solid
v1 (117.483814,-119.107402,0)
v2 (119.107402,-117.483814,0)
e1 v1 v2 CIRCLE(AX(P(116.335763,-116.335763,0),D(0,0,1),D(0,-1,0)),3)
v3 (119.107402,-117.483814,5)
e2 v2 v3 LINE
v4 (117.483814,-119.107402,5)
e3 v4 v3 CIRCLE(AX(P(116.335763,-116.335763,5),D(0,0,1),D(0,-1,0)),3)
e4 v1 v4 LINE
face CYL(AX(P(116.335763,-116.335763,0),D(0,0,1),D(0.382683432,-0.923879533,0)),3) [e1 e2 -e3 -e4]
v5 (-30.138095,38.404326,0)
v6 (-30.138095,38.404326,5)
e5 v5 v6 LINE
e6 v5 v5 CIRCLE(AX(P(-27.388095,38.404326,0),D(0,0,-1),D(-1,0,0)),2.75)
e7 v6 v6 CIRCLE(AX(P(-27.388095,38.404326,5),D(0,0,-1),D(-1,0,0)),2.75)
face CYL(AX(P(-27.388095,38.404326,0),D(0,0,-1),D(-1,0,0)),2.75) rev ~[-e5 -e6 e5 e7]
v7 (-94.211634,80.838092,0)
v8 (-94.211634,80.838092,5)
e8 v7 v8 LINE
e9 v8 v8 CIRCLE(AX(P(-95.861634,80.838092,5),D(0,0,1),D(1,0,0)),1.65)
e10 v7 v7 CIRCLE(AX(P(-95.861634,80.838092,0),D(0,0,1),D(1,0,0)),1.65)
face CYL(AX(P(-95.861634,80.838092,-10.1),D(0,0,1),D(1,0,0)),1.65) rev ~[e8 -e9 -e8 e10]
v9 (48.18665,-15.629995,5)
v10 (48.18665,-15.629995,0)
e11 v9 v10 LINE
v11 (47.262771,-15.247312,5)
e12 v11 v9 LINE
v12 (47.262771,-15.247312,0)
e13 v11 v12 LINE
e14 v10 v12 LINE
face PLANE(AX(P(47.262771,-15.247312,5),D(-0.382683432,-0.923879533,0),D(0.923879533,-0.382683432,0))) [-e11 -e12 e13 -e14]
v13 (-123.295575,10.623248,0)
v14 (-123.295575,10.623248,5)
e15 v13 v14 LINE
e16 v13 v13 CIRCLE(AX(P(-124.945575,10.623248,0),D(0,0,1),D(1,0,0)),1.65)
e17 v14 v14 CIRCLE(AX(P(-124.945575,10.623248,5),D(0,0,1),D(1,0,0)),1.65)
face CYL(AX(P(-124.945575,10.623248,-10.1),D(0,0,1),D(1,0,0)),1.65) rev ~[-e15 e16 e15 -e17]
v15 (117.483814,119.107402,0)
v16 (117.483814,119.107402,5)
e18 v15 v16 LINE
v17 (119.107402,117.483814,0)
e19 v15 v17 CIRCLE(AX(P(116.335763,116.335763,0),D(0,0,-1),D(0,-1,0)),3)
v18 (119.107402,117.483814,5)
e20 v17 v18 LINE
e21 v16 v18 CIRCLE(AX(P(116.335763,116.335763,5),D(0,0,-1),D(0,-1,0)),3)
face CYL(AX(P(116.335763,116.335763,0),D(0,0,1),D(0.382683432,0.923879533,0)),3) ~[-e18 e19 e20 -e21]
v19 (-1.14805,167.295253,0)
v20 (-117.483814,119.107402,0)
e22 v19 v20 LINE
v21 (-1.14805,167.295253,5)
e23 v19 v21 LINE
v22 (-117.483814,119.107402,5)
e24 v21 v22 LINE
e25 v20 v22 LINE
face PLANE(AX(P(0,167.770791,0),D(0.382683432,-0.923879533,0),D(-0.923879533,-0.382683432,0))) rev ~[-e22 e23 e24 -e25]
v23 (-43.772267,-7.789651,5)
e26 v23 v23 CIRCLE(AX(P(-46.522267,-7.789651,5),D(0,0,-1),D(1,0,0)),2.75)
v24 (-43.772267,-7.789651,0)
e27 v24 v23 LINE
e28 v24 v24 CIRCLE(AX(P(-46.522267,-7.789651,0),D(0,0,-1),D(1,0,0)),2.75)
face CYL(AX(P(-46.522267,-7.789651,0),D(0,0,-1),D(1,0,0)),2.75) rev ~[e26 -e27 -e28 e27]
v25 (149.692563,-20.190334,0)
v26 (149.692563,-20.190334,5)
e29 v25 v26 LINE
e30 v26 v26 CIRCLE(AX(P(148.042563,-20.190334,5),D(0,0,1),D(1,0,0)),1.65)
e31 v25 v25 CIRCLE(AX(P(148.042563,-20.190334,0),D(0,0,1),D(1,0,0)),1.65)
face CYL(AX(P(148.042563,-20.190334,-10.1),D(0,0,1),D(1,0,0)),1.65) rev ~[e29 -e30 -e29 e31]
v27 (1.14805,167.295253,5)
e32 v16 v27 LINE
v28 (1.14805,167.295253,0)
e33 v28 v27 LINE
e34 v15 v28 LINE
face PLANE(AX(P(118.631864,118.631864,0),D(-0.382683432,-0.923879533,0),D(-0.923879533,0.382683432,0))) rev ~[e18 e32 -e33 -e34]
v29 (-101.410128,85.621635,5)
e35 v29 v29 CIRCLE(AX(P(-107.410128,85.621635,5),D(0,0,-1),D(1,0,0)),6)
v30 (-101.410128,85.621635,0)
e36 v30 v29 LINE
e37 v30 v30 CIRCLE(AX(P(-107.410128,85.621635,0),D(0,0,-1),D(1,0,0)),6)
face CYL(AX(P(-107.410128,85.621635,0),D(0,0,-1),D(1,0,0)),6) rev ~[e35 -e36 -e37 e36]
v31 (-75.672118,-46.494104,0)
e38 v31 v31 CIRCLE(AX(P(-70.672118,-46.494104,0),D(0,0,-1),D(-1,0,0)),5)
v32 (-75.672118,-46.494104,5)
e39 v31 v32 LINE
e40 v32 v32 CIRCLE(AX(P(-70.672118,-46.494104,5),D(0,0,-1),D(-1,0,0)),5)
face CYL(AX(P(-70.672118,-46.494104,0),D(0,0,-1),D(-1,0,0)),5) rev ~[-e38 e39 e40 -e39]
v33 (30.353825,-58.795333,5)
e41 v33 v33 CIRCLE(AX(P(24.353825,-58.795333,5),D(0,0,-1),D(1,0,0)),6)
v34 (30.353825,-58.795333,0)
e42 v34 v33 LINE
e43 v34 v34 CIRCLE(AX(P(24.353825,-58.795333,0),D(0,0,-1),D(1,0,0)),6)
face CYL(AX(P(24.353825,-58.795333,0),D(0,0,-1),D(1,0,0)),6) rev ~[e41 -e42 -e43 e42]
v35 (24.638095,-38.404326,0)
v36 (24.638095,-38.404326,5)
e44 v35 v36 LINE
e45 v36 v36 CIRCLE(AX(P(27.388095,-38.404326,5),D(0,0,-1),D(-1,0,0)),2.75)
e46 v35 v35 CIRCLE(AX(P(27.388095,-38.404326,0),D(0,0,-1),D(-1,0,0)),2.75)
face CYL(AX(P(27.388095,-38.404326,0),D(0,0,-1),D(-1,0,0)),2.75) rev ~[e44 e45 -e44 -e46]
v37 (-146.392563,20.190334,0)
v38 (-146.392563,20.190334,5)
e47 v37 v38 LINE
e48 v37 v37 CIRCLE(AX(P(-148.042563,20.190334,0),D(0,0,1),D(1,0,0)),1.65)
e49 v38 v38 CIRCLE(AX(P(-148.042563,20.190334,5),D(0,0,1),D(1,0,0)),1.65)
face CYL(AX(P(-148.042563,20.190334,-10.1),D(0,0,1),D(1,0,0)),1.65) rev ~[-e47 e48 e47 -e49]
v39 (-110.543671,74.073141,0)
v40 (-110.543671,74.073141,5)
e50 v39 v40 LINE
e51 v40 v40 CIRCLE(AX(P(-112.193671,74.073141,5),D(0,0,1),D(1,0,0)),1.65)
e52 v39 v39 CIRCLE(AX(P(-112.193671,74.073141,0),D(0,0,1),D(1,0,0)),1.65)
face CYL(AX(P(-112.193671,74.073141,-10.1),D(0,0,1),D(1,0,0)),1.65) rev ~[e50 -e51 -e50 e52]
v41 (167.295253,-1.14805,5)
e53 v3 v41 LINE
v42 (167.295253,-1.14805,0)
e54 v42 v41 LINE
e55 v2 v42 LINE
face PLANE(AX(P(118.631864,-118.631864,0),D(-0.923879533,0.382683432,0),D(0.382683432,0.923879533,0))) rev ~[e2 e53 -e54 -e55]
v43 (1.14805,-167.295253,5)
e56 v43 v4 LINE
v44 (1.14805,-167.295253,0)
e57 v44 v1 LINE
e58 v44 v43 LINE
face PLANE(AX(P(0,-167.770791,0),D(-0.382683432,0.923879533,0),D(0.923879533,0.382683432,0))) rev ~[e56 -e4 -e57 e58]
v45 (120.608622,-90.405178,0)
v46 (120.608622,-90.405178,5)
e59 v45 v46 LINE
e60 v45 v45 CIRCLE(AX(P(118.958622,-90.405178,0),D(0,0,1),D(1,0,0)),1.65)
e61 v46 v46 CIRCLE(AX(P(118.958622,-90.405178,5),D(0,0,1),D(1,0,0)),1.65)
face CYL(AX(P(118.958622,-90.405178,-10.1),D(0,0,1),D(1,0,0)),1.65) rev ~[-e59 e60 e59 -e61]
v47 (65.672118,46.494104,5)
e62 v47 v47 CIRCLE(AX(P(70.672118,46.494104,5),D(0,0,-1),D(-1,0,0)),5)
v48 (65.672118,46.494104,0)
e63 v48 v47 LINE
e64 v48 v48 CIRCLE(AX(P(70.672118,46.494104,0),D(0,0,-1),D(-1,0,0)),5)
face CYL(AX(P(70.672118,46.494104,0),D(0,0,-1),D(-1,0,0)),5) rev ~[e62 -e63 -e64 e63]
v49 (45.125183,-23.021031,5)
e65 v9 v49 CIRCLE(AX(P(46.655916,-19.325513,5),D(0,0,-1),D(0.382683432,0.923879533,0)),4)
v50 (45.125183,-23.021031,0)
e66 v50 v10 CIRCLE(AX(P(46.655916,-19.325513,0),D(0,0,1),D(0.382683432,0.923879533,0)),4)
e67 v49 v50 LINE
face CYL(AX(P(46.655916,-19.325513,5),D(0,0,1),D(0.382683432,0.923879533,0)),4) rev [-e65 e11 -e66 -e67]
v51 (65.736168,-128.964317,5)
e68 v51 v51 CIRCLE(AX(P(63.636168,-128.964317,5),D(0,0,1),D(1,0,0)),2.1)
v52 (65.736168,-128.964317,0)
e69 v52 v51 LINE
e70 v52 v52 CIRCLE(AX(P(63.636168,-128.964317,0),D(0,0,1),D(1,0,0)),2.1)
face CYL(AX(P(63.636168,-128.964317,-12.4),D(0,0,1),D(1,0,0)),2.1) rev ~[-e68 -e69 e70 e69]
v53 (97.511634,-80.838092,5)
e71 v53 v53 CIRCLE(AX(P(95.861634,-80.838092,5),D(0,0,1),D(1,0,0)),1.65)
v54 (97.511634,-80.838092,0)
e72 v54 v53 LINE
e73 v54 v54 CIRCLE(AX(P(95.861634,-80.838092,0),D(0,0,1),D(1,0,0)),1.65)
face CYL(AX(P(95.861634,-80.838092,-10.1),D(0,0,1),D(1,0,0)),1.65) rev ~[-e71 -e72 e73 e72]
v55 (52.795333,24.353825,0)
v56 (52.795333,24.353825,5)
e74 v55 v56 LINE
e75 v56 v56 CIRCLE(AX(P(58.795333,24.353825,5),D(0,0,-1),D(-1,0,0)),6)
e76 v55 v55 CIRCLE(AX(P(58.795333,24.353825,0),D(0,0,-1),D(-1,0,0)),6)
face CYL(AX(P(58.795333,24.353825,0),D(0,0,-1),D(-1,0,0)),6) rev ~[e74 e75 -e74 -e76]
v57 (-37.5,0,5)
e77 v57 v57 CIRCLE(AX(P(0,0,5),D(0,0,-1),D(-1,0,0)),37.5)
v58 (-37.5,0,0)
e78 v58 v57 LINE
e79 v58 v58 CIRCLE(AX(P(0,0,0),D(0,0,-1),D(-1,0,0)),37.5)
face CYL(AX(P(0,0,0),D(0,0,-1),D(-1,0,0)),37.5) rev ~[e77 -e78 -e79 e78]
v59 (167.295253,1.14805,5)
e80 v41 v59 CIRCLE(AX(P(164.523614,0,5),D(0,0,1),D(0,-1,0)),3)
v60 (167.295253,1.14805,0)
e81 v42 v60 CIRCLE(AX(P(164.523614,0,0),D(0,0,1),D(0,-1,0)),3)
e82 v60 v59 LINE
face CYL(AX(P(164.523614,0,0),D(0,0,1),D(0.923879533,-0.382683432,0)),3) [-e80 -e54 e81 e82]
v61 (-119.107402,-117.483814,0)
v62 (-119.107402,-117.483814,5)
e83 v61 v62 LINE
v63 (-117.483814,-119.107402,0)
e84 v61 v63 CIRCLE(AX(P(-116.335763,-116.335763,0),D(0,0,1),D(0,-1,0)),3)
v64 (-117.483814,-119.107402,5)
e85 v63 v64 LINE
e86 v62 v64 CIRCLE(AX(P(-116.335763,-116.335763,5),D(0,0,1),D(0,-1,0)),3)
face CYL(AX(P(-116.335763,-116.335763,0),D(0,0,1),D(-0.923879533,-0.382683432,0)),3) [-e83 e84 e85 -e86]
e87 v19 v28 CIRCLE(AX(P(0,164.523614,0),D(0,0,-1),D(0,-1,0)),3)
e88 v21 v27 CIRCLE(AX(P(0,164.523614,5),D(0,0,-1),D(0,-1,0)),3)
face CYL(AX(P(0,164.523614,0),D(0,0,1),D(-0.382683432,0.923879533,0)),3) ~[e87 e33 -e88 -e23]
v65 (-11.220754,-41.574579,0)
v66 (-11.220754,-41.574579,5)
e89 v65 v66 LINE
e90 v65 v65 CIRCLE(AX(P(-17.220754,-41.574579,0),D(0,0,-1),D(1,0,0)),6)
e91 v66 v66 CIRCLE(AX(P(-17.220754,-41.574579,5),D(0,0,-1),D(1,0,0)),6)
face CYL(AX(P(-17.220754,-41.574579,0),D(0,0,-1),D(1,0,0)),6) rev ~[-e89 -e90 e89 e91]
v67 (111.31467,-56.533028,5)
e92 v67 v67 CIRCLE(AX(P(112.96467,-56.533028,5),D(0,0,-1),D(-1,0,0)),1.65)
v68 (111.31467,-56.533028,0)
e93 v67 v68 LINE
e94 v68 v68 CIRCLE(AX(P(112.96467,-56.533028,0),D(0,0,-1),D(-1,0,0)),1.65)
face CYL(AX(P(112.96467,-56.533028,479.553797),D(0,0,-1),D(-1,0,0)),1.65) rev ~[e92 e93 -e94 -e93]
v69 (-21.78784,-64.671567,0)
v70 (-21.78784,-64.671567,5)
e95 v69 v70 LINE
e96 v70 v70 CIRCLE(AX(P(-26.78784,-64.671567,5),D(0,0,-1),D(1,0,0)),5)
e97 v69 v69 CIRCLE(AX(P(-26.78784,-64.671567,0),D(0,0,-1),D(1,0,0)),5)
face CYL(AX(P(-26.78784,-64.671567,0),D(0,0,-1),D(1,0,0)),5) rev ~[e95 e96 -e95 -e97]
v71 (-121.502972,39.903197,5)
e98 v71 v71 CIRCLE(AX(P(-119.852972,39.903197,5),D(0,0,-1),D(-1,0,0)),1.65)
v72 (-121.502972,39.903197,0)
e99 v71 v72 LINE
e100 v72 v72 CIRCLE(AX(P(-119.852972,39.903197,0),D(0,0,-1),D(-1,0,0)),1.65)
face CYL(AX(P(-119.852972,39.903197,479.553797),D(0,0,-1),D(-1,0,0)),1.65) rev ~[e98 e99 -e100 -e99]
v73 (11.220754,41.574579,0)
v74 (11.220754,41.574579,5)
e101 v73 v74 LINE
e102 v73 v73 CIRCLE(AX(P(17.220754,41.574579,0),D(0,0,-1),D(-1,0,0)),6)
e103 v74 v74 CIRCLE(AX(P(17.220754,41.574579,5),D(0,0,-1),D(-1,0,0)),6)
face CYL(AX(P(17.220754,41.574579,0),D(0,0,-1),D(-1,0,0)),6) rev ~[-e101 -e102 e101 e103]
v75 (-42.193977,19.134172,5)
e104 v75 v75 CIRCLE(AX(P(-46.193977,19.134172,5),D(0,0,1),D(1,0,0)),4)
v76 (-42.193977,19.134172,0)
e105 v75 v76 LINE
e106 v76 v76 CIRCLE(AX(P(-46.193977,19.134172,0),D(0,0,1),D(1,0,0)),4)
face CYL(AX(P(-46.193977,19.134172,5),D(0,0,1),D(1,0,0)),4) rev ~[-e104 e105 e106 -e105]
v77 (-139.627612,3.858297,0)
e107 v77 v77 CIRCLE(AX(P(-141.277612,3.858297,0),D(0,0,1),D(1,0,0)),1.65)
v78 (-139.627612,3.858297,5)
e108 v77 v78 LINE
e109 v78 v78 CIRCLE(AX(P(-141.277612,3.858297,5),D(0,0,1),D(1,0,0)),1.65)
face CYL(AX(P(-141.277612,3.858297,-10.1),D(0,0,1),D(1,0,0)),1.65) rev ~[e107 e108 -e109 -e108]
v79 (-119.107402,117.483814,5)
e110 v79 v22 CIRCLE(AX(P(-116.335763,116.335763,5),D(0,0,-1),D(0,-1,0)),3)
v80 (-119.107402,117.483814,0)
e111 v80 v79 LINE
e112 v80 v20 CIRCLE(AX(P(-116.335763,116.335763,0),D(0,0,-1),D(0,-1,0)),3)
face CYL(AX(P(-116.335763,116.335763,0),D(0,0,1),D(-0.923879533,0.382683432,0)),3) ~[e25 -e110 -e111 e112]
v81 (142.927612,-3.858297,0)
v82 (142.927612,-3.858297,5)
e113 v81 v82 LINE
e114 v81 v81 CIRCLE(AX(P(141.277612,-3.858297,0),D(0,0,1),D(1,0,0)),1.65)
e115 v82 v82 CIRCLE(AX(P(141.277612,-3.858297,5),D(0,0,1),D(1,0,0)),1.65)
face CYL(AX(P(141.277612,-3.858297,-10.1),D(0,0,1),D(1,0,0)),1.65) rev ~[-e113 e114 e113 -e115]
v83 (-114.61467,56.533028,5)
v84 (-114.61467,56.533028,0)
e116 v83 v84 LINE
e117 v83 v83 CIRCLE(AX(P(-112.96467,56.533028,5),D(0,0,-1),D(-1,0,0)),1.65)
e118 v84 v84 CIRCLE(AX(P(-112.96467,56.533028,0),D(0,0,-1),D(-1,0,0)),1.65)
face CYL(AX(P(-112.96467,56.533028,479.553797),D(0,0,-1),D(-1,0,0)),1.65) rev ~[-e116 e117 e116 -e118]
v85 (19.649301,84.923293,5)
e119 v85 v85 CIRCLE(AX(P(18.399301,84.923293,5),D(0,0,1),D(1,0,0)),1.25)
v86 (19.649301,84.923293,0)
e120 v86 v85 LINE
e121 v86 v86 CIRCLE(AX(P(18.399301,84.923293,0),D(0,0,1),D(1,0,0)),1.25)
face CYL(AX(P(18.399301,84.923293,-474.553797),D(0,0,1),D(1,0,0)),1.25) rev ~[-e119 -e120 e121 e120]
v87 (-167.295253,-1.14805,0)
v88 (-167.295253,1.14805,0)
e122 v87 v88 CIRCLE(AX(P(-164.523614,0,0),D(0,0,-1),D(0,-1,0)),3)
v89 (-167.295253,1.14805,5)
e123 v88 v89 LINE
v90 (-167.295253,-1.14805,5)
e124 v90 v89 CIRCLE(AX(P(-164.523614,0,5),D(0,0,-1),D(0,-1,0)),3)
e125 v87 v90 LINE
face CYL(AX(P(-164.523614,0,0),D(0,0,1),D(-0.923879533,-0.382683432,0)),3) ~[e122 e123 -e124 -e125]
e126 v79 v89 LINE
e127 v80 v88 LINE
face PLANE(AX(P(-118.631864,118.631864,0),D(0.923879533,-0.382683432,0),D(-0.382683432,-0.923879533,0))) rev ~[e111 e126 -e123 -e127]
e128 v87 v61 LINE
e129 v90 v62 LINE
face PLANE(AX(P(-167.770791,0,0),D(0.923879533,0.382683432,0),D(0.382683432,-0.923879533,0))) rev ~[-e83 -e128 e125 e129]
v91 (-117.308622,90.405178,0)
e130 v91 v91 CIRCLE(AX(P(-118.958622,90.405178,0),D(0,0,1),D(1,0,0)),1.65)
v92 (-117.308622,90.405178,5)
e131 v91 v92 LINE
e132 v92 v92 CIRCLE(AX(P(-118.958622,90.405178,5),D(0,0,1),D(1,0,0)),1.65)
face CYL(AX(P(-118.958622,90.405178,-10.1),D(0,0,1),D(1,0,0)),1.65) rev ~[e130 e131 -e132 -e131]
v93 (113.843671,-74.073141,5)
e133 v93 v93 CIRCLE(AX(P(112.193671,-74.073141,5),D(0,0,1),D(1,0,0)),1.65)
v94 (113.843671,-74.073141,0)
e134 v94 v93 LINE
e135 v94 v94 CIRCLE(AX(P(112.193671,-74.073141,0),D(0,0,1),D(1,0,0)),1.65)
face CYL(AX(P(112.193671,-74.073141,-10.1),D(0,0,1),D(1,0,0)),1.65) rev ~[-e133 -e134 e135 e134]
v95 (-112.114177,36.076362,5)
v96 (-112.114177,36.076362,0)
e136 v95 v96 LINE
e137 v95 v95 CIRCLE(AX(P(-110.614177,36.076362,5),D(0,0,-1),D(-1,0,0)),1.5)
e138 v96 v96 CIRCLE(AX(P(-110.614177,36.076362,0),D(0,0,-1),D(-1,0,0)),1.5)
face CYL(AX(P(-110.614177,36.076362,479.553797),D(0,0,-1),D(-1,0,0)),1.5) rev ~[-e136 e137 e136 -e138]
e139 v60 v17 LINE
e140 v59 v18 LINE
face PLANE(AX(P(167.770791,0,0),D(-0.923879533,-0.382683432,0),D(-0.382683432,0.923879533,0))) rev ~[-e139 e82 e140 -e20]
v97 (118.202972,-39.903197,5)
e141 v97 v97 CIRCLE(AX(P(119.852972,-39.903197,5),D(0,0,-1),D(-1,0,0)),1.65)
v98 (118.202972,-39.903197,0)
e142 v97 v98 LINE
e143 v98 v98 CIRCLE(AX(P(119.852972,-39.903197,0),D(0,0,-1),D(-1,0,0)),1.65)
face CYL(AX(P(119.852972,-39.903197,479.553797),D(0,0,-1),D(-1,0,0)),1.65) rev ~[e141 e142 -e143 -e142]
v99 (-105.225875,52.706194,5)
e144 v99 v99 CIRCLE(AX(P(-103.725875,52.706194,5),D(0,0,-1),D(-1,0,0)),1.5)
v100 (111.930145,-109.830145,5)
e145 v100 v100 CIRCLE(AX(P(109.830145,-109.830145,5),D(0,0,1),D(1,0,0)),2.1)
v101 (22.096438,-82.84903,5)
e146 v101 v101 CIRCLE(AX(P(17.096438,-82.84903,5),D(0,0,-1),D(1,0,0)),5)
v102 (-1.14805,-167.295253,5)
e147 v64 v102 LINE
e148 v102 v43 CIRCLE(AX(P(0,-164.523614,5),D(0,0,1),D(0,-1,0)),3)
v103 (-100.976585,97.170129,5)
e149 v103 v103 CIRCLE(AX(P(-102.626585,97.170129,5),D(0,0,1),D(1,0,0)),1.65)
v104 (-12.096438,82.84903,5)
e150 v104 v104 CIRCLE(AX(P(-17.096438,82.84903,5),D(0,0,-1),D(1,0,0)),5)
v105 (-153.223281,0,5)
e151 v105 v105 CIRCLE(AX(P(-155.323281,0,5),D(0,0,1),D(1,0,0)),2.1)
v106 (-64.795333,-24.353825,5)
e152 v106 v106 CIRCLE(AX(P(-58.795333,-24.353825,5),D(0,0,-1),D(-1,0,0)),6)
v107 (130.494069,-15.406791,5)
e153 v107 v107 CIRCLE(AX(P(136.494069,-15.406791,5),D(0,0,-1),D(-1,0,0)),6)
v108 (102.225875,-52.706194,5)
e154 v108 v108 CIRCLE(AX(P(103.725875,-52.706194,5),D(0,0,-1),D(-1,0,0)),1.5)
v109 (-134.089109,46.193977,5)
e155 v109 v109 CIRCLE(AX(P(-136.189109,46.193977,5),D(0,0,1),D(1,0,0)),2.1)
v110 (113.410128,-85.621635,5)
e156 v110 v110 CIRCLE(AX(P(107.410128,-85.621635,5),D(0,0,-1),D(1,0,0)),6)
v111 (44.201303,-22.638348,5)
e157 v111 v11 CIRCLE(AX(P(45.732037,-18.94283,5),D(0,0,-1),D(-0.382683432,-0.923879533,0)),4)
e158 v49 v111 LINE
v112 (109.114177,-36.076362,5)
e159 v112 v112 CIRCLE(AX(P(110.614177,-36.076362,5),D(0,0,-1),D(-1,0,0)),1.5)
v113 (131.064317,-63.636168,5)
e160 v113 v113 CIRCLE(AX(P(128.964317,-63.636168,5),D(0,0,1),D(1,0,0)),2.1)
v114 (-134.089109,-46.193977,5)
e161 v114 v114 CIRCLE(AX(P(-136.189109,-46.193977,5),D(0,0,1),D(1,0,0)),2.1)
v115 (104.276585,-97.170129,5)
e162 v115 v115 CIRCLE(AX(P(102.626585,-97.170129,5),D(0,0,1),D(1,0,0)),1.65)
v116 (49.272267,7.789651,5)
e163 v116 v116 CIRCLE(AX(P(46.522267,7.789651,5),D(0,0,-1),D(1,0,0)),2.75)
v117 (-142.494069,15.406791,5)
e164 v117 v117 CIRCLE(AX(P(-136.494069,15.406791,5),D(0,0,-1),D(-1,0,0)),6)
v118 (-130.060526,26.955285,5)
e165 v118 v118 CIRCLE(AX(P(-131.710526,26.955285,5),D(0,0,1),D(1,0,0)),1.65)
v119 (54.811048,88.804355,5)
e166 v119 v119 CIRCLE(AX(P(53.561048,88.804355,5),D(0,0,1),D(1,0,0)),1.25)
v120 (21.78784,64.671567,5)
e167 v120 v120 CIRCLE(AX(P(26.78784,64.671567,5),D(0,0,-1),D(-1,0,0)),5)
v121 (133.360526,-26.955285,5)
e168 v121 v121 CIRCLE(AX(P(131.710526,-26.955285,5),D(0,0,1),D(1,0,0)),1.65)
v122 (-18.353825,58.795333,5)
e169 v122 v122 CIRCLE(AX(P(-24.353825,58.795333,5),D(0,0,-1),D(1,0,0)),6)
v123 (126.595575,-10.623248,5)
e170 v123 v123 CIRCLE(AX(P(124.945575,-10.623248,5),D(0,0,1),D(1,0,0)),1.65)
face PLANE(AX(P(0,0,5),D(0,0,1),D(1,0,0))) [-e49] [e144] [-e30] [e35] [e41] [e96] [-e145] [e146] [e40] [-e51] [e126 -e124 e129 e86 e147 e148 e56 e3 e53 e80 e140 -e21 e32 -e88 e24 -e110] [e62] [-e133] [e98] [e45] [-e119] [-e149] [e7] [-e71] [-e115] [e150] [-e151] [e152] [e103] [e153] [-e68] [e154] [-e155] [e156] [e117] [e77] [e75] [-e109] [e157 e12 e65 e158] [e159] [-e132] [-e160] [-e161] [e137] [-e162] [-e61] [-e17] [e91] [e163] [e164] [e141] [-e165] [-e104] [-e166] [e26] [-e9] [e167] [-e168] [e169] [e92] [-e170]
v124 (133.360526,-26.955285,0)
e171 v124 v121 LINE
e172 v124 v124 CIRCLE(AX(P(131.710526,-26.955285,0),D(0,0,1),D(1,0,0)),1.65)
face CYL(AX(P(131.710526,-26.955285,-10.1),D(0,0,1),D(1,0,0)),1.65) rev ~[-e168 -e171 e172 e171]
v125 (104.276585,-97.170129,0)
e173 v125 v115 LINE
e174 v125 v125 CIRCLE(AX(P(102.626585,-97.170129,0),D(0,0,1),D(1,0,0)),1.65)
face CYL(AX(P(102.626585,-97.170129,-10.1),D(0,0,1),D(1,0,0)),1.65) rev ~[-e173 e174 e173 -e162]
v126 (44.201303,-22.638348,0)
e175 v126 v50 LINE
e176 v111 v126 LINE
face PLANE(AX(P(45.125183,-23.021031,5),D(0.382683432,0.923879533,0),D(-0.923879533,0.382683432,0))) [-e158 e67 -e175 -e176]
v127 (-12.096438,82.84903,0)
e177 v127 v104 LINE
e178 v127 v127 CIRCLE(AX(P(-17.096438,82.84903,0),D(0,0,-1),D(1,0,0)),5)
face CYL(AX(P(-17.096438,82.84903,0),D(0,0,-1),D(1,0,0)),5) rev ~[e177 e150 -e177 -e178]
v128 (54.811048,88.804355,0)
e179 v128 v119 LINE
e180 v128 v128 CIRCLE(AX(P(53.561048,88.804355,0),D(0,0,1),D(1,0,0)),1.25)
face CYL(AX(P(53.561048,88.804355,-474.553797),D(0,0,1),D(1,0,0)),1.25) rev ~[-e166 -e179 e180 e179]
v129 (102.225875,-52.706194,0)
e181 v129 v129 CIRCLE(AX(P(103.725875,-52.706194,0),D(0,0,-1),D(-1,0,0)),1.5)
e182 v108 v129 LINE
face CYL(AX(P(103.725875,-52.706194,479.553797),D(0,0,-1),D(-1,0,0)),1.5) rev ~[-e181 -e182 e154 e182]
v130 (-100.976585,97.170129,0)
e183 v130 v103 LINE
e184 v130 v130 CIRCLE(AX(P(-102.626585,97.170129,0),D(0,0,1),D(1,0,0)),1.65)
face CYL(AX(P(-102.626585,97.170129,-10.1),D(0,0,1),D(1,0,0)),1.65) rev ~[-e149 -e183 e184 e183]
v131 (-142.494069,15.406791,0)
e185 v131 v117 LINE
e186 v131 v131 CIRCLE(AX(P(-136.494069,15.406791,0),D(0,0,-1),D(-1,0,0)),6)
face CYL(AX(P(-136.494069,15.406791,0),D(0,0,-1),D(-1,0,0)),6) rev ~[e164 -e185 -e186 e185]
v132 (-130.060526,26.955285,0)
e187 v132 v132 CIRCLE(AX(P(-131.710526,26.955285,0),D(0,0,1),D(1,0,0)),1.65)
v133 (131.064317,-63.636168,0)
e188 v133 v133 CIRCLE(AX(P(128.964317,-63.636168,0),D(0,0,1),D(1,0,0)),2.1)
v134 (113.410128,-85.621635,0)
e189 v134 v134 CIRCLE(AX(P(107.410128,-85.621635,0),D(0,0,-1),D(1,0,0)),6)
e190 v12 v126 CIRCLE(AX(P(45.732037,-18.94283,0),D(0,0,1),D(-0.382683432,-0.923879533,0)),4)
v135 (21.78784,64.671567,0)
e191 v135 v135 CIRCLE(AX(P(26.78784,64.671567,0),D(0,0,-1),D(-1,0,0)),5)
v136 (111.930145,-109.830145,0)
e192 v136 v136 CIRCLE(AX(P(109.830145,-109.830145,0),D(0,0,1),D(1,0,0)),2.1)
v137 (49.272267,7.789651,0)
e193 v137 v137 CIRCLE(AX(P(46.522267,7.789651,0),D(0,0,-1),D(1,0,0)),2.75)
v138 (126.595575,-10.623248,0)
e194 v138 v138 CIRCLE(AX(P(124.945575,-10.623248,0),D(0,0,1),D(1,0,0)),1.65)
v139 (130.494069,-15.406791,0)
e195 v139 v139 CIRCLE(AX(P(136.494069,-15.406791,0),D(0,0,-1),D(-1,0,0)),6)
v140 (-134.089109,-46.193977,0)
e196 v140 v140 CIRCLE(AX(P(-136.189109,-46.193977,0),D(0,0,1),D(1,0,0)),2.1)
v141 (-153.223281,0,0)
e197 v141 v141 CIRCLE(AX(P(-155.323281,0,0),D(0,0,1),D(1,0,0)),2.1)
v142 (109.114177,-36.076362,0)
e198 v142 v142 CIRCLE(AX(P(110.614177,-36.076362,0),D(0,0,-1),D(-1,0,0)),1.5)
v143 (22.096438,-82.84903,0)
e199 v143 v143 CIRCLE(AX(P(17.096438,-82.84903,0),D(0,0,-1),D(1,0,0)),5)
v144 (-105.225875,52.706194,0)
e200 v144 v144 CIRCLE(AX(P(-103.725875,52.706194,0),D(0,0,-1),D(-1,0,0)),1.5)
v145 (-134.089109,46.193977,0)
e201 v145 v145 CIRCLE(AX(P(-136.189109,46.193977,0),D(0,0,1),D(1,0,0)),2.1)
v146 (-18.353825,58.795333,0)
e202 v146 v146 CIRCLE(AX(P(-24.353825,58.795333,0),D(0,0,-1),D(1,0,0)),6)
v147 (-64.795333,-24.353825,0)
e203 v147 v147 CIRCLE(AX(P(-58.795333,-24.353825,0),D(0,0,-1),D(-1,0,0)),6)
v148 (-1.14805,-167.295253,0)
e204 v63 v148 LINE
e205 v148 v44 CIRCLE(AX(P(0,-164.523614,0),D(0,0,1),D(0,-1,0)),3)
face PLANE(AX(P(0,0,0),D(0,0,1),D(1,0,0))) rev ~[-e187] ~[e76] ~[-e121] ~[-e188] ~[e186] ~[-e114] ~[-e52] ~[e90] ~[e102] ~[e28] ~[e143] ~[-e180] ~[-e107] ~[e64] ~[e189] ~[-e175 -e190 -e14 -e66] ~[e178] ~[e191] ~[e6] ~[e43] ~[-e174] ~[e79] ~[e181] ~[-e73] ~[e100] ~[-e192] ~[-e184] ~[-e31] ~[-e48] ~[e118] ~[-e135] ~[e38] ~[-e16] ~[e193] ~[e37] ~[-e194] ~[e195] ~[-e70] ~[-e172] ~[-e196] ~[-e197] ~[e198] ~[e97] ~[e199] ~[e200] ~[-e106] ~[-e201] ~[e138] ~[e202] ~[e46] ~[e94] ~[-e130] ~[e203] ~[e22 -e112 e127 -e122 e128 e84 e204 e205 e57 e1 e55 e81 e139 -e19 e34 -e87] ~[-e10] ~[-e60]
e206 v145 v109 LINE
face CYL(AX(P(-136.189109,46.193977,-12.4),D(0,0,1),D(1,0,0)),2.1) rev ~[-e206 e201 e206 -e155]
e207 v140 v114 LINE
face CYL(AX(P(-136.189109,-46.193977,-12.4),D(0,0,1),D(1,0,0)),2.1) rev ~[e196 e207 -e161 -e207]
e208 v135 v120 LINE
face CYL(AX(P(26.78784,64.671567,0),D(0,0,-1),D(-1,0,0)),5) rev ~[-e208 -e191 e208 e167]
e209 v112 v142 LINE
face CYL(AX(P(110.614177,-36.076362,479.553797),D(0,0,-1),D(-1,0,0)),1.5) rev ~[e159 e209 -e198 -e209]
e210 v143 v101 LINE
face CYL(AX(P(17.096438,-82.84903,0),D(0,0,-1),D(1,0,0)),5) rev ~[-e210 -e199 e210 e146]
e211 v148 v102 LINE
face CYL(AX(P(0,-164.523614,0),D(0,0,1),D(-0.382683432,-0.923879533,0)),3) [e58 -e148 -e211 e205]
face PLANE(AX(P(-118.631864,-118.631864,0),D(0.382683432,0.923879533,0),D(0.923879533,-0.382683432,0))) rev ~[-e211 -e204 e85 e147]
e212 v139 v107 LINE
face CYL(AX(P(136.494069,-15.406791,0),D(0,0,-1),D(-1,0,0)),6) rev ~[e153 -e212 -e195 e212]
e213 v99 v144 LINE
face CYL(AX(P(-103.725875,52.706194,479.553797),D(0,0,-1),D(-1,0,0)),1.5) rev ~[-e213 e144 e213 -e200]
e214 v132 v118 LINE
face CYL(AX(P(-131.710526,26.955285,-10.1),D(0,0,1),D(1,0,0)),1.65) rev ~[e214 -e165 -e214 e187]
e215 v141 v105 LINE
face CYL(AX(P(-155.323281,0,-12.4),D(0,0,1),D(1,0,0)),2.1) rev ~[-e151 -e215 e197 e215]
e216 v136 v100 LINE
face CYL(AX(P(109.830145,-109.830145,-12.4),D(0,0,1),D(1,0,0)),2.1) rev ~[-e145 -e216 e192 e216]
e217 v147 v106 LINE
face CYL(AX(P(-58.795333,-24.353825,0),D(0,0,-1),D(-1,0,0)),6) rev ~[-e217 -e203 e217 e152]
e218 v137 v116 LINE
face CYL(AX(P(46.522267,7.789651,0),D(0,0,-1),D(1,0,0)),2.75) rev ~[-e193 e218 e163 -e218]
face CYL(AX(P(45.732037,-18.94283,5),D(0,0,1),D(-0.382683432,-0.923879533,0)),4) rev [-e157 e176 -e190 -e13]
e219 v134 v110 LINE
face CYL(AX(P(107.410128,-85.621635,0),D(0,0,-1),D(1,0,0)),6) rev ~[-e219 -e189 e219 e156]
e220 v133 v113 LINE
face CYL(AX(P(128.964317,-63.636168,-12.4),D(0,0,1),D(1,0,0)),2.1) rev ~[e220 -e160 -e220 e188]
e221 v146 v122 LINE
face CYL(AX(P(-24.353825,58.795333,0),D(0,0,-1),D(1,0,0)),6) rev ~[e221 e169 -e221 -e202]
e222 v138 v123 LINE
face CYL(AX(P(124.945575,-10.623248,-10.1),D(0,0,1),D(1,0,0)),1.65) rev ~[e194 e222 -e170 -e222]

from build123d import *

# Parameters (mm, degrees)
BOSS_EXTRUDE1_DEPTH      = 5
SKETCH2_R                = 37.5
CUT_EXTRUDE1_DEPTH       = 10
SKETCH3_R                = 1
CUT_EXTRUDE2_DEPTH       = 10
M5_TAPPED_HOLE1_D        = 4.2
M5_TAPPED_HOLE1_DEPTH    = 12.4
M5_TAPPED_HOLE1_TIP      = 1.2618073
SKETCH5_R                = 2.75
CUT_EXTRUDE3_DEPTH       = 10
SKETCH6_R                = 5
CUT_EXTRUDE4_DEPTH       = 55
SKETCH7_R                = 4
CUT_EXTRUDE5_DEPTH       = 15
SKETCH8_R                = 6
CUT_EXTRUDE6_DEPTH       = 10
SKETCH9_R                = 6
CUT_EXTRUDE7_DEPTH       = 10
SKETCH10_R               = 1
CUT_EXTRUDE8_DEPTH       = 10
M4_TAPPED_HOLE1_D        = 3.3
M4_TAPPED_HOLE1_DEPTH    = 10.1
M4_TAPPED_HOLE1_TIP      = 0.991420021
M4_TAPPED_HOLE2_D        = 3.3
F_3_0_3_DIAMETER_HOLE1_D = 3
M3_TAPPED_HOLE1_D        = 2.5
FILLET1_R                = 3
CUT_EXTRUDE9_DEPTH       = 237.966923416


with BuildPart() as part:
    # Sketch1 → Boss-Extrude1 (new body)
    with BuildSketch(Plane.XY):
        Polygon((-167.770791045, 0), (-118.631864033, -118.631864033), (0, -167.770791045), (118.631864033, -118.631864033), (167.770791045, 0), (118.631864033, 118.631864033), (0, 167.770791045), (-118.631864033, 118.631864033), align=None)
    extrude(amount=BOSS_EXTRUDE1_DEPTH)

    # Sketch2 → Cut-Extrude1 (cut)
    with BuildSketch(Plane(origin=(0, 0, 0), x_dir=(-1, 0, 0), z_dir=(0, 0, -1))):
        Circle(SKETCH2_R)
    extrude(amount=-CUT_EXTRUDE1_DEPTH, mode=Mode.SUBTRACT)

    # Sketch3 → Cut-Extrude2 (cut)
    with BuildSketch(Plane.XY.offset(5)):
        with Locations((-136.189109124, 46.193976626)):
            Circle(SKETCH3_R)
        with Locations((-155.323280742, 0)):
            Circle(SKETCH3_R)
        with Locations((-136.189109124, -46.193976626)):
            Circle(SKETCH3_R)
        with Locations((63.636168463, -128.964316707)):
            Circle(SKETCH3_R)
        with Locations((109.830145089, -109.830145089)):
            Circle(SKETCH3_R)
        with Locations((128.964316707, -63.636168463)):
            Circle(SKETCH3_R)
    extrude(amount=-CUT_EXTRUDE2_DEPTH, mode=Mode.SUBTRACT)

    # M5 Tapped Hole1
    with Locations(Plane(origin=(-136.189109124, 46.193976626, 0), x_dir=(-1, 0, 0), z_dir=(0, 0, -1))):
        with Locations((0, 0), (19.134171618, -46.193976626), (-246.019254213, -156.024121715), (-265.153425831, -109.830145089), (-199.825277587, -175.158293333), (0, -92.387953252)):
            Hole(M5_TAPPED_HOLE1_D / 2, depth=M5_TAPPED_HOLE1_DEPTH)
            with Locations((0, 0, -(M5_TAPPED_HOLE1_DEPTH + M5_TAPPED_HOLE1_TIP / 2))):  # 118° drill point
                Cone(0, M5_TAPPED_HOLE1_D / 2, M5_TAPPED_HOLE1_TIP, mode=Mode.SUBTRACT)

    # Sketch5 → Cut-Extrude3 (cut)
    with BuildSketch(Plane(origin=(0, 0, 0), x_dir=(-1, 0, 0), z_dir=(0, 0, -1))):
        with Locations((-27.388095491, -38.404325607)):
            Circle(SKETCH5_R)
        with Locations(Location((46.52226711, -7.789651018, 0), (0, 0, 180))):
            Circle(SKETCH5_R)
        with Locations((27.388095491, 38.404325607)):
            Circle(SKETCH5_R)
        with Locations(Location((-46.52226711, 7.789651018, 0), (0, 0, 180))):
            Circle(SKETCH5_R)
    extrude(amount=-CUT_EXTRUDE3_DEPTH, mode=Mode.SUBTRACT)

    # Sketch6 → Cut-Extrude4 (cut)
    with BuildSketch(Plane(origin=(0, 0, 0), x_dir=(-1, 0, 0), z_dir=(0, 0, -1))):
        with Locations((-70.67211806, 46.494104238)):
            Circle(SKETCH6_R)
        with Locations((-26.787840266, 64.671567276)):
            Circle(SKETCH6_R)
        with Locations(Location((17.096437529, 82.849030313, 0), (0, 0, 180))):
            Circle(SKETCH6_R)
        with Locations((70.67211806, -46.494104238)):
            Circle(SKETCH6_R)
        with Locations(Location((26.787840266, -64.671567276, 0), (0, 0, 180))):
            Circle(SKETCH6_R)
        with Locations(Location((-17.096437529, -82.849030313, 0), (0, 0, 180))):
            Circle(SKETCH6_R)
    extrude(amount=-CUT_EXTRUDE4_DEPTH, mode=Mode.SUBTRACT)

    # Sketch7 → Cut-Extrude5 (cut)
    with BuildSketch(Plane.XY.offset(5)):
        with Locations((46.193976626, -19.134171618)):
            Circle(SKETCH7_R)
        with Locations((-46.193976626, 19.134171618)):
            Circle(SKETCH7_R)
    extrude(amount=-CUT_EXTRUDE5_DEPTH, mode=Mode.SUBTRACT)

    # Sketch8 → Cut-Extrude6 (cut)
    with BuildSketch(Plane(origin=(0, 0, 0), x_dir=(-1, 0, 0), z_dir=(0, 0, -1))):
        with Locations((-58.795333419, 24.353824507)):
            Circle(SKETCH8_R)
        with Locations((-17.220754456, 41.574578963)):
            Circle(SKETCH8_R)
        with Locations(Location((24.353824507, 58.795333419, 0), (0, 0, 180))):
            Circle(SKETCH8_R)
        with Locations((58.795333419, -24.353824507)):
            Circle(SKETCH8_R)
        with Locations(Location((17.220754456, -41.574578963, 0), (0, 0, 180))):
            Circle(SKETCH8_R)
        with Locations(Location((-24.353824507, -58.795333419, 0), (0, 0, 180))):
            Circle(SKETCH8_R)
    extrude(amount=-CUT_EXTRUDE6_DEPTH, mode=Mode.SUBTRACT)

    # Sketch9 → Cut-Extrude7 (cut)
    with BuildSketch(Plane(origin=(0, 0, 0), x_dir=(-1, 0, 0), z_dir=(0, 0, -1))):
        with Locations((-136.494068721, -15.406790837)):
            Circle(SKETCH9_R)
        with Locations(Location((-107.410127862, -85.621635308, 0), (0, 0, 180))):
            Circle(SKETCH9_R)
        with Locations((136.494068721, 15.406790837)):
            Circle(SKETCH9_R)
        with Locations(Location((107.410127862, 85.621635308, 0), (0, 0, 180))):
            Circle(SKETCH9_R)
    extrude(amount=-CUT_EXTRUDE7_DEPTH, mode=Mode.SUBTRACT)

    # Sketch10 → Cut-Extrude8 (cut)
    with BuildSketch(Plane(origin=(0, 0, 0), x_dir=(-1, 0, 0), z_dir=(0, 0, -1))):
        with Locations((-141.277611626, -3.85829668)):
            Circle(SKETCH10_R)
        with Locations(Location((-131.710525817, -26.955284993, 0), (0, 0, 180))):
            Circle(SKETCH10_R)
        with Locations((-148.042562878, -20.190333741)):
            Circle(SKETCH10_R)
        with Locations(Location((-124.945574565, -10.623247932, 0), (0, 0, 180))):
            Circle(SKETCH10_R)
        with Locations(Location((-118.958622018, -90.405178212, 0), (0, 0, 180))):
            Circle(SKETCH10_R)
        with Locations((-112.193670766, -74.073141151)):
            Circle(SKETCH10_R)
        with Locations((-95.861633705, -80.838092403)):
            Circle(SKETCH10_R)
        with Locations(Location((-102.626584957, -97.170129464, 0), (0, 0, 180))):
            Circle(SKETCH10_R)
        with Locations((148.042562878, 20.190333741)):
            Circle(SKETCH10_R)
        with Locations(Location((131.710525817, 26.955284993, 0), (0, 0, 180))):
            Circle(SKETCH10_R)
        with Locations(Location((124.945574565, 10.623247932, 0), (0, 0, 180))):
            Circle(SKETCH10_R)
        with Locations((141.277611626, 3.85829668)):
            Circle(SKETCH10_R)
        with Locations(Location((118.958622018, 90.405178212, 0), (0, 0, 180))):
            Circle(SKETCH10_R)
        with Locations((95.861633705, 80.838092403)):
            Circle(SKETCH10_R)
        with Locations(Location((102.626584957, 97.170129464, 0), (0, 0, 180))):
            Circle(SKETCH10_R)
        with Locations((112.193670766, 74.073141151)):
            Circle(SKETCH10_R)
    extrude(amount=-CUT_EXTRUDE8_DEPTH, mode=Mode.SUBTRACT)

    # M4 Tapped Hole1
    with Locations(Plane(origin=(141.277611626, -3.85829668, 0), x_dir=(-1, 0, 0), z_dir=(0, 0, -1))):
        with Locations((0, 0), (-6.764951252, -16.332037061), (16.332037061, -6.764951252), (9.567085809, -23.096988313), (29.08394086, -70.214844471), (22.318989608, -86.546881532), (38.651026669, -93.311832784), (45.415977921, -76.979795723), (282.555223252, 7.71659336), (289.320174504, 24.048630421), (272.988137443, 30.813581673), (266.223186191, 14.481544612), (243.904196583, 101.028426144), (253.471282392, 77.931437831), (260.236233644, 94.263474892), (237.139245331, 84.696389083)):
            Hole(M4_TAPPED_HOLE1_D / 2, depth=M4_TAPPED_HOLE1_DEPTH)
            with Locations((0, 0, -(M4_TAPPED_HOLE1_DEPTH + M4_TAPPED_HOLE1_TIP / 2))):  # 118° drill point
                Cone(0, M4_TAPPED_HOLE1_D / 2, M4_TAPPED_HOLE1_TIP, mode=Mode.SUBTRACT)

    # M4 Tapped Hole2 (through all)
    with Locations(Plane.XY.offset(5)):
        with Locations((-112.964670205, 56.533028271), (-119.852971988, 39.903196685), (119.852971988, -39.903196685), (112.964670205, -56.533028271)):
            Hole(M4_TAPPED_HOLE2_D / 2)

    # Ø3.0 (3) Diameter Hole1 (through all)
    with Locations(Plane.XY.offset(5)):
        with Locations((110.614176663, -36.076362362), (103.72587488, -52.706193947), (-103.72587488, 52.706193947), (-110.614176663, 36.076362362)):
            Hole(F_3_0_3_DIAMETER_HOLE1_D / 2)

    # M3 Tapped Hole1 (through all)
    with Locations(Plane(origin=(0, 0, 0), x_dir=(-1, 0, 0), z_dir=(0, 0, -1))):
        with Locations((-18.399300713, 84.923293231), (-53.561047521, 88.804355428)):
            Hole(M3_TAPPED_HOLE1_D / 2)

    # Fillet1
    fillet1_edges = [part.edges().sort_by_distance(p)[0] for p in [
        (-118.631864033, -118.631864033, 2.5),
        (-167.770791045, 0, 2.5),
        (-118.631864033, 118.631864033, 2.5),
        (0, 167.770791045, 2.5),
        (118.631864033, 118.631864033, 2.5),
        (167.770791045, 0, 2.5),
        (118.631864033, -118.631864033, 2.5),
        (0, -167.770791045, 2.5),
    ]]
    fillet(fillet1_edges, radius=FILLET1_R)

    # Sketch20 → Cut-Extrude9 (cut, through all)
    with BuildSketch(Plane.XY.offset(5)):
        with BuildLine():
            Line((47.262770589, -15.247311772), (48.186650121, -15.629995204))
            ThreePointArc((48.186650121, -15.629995204), (50.351434522, -20.856247064), (45.125182662, -23.021031464))
            Line((45.125182662, -23.021031464), (44.20130313, -22.638348032))
            ThreePointArc((44.20130313, -22.638348032), (42.036518729, -17.412096173), (47.262770589, -15.247311772))
        make_face()
    extrude(amount=-CUT_EXTRUDE9_DEPTH, mode=Mode.SUBTRACT)


solid = part.part
